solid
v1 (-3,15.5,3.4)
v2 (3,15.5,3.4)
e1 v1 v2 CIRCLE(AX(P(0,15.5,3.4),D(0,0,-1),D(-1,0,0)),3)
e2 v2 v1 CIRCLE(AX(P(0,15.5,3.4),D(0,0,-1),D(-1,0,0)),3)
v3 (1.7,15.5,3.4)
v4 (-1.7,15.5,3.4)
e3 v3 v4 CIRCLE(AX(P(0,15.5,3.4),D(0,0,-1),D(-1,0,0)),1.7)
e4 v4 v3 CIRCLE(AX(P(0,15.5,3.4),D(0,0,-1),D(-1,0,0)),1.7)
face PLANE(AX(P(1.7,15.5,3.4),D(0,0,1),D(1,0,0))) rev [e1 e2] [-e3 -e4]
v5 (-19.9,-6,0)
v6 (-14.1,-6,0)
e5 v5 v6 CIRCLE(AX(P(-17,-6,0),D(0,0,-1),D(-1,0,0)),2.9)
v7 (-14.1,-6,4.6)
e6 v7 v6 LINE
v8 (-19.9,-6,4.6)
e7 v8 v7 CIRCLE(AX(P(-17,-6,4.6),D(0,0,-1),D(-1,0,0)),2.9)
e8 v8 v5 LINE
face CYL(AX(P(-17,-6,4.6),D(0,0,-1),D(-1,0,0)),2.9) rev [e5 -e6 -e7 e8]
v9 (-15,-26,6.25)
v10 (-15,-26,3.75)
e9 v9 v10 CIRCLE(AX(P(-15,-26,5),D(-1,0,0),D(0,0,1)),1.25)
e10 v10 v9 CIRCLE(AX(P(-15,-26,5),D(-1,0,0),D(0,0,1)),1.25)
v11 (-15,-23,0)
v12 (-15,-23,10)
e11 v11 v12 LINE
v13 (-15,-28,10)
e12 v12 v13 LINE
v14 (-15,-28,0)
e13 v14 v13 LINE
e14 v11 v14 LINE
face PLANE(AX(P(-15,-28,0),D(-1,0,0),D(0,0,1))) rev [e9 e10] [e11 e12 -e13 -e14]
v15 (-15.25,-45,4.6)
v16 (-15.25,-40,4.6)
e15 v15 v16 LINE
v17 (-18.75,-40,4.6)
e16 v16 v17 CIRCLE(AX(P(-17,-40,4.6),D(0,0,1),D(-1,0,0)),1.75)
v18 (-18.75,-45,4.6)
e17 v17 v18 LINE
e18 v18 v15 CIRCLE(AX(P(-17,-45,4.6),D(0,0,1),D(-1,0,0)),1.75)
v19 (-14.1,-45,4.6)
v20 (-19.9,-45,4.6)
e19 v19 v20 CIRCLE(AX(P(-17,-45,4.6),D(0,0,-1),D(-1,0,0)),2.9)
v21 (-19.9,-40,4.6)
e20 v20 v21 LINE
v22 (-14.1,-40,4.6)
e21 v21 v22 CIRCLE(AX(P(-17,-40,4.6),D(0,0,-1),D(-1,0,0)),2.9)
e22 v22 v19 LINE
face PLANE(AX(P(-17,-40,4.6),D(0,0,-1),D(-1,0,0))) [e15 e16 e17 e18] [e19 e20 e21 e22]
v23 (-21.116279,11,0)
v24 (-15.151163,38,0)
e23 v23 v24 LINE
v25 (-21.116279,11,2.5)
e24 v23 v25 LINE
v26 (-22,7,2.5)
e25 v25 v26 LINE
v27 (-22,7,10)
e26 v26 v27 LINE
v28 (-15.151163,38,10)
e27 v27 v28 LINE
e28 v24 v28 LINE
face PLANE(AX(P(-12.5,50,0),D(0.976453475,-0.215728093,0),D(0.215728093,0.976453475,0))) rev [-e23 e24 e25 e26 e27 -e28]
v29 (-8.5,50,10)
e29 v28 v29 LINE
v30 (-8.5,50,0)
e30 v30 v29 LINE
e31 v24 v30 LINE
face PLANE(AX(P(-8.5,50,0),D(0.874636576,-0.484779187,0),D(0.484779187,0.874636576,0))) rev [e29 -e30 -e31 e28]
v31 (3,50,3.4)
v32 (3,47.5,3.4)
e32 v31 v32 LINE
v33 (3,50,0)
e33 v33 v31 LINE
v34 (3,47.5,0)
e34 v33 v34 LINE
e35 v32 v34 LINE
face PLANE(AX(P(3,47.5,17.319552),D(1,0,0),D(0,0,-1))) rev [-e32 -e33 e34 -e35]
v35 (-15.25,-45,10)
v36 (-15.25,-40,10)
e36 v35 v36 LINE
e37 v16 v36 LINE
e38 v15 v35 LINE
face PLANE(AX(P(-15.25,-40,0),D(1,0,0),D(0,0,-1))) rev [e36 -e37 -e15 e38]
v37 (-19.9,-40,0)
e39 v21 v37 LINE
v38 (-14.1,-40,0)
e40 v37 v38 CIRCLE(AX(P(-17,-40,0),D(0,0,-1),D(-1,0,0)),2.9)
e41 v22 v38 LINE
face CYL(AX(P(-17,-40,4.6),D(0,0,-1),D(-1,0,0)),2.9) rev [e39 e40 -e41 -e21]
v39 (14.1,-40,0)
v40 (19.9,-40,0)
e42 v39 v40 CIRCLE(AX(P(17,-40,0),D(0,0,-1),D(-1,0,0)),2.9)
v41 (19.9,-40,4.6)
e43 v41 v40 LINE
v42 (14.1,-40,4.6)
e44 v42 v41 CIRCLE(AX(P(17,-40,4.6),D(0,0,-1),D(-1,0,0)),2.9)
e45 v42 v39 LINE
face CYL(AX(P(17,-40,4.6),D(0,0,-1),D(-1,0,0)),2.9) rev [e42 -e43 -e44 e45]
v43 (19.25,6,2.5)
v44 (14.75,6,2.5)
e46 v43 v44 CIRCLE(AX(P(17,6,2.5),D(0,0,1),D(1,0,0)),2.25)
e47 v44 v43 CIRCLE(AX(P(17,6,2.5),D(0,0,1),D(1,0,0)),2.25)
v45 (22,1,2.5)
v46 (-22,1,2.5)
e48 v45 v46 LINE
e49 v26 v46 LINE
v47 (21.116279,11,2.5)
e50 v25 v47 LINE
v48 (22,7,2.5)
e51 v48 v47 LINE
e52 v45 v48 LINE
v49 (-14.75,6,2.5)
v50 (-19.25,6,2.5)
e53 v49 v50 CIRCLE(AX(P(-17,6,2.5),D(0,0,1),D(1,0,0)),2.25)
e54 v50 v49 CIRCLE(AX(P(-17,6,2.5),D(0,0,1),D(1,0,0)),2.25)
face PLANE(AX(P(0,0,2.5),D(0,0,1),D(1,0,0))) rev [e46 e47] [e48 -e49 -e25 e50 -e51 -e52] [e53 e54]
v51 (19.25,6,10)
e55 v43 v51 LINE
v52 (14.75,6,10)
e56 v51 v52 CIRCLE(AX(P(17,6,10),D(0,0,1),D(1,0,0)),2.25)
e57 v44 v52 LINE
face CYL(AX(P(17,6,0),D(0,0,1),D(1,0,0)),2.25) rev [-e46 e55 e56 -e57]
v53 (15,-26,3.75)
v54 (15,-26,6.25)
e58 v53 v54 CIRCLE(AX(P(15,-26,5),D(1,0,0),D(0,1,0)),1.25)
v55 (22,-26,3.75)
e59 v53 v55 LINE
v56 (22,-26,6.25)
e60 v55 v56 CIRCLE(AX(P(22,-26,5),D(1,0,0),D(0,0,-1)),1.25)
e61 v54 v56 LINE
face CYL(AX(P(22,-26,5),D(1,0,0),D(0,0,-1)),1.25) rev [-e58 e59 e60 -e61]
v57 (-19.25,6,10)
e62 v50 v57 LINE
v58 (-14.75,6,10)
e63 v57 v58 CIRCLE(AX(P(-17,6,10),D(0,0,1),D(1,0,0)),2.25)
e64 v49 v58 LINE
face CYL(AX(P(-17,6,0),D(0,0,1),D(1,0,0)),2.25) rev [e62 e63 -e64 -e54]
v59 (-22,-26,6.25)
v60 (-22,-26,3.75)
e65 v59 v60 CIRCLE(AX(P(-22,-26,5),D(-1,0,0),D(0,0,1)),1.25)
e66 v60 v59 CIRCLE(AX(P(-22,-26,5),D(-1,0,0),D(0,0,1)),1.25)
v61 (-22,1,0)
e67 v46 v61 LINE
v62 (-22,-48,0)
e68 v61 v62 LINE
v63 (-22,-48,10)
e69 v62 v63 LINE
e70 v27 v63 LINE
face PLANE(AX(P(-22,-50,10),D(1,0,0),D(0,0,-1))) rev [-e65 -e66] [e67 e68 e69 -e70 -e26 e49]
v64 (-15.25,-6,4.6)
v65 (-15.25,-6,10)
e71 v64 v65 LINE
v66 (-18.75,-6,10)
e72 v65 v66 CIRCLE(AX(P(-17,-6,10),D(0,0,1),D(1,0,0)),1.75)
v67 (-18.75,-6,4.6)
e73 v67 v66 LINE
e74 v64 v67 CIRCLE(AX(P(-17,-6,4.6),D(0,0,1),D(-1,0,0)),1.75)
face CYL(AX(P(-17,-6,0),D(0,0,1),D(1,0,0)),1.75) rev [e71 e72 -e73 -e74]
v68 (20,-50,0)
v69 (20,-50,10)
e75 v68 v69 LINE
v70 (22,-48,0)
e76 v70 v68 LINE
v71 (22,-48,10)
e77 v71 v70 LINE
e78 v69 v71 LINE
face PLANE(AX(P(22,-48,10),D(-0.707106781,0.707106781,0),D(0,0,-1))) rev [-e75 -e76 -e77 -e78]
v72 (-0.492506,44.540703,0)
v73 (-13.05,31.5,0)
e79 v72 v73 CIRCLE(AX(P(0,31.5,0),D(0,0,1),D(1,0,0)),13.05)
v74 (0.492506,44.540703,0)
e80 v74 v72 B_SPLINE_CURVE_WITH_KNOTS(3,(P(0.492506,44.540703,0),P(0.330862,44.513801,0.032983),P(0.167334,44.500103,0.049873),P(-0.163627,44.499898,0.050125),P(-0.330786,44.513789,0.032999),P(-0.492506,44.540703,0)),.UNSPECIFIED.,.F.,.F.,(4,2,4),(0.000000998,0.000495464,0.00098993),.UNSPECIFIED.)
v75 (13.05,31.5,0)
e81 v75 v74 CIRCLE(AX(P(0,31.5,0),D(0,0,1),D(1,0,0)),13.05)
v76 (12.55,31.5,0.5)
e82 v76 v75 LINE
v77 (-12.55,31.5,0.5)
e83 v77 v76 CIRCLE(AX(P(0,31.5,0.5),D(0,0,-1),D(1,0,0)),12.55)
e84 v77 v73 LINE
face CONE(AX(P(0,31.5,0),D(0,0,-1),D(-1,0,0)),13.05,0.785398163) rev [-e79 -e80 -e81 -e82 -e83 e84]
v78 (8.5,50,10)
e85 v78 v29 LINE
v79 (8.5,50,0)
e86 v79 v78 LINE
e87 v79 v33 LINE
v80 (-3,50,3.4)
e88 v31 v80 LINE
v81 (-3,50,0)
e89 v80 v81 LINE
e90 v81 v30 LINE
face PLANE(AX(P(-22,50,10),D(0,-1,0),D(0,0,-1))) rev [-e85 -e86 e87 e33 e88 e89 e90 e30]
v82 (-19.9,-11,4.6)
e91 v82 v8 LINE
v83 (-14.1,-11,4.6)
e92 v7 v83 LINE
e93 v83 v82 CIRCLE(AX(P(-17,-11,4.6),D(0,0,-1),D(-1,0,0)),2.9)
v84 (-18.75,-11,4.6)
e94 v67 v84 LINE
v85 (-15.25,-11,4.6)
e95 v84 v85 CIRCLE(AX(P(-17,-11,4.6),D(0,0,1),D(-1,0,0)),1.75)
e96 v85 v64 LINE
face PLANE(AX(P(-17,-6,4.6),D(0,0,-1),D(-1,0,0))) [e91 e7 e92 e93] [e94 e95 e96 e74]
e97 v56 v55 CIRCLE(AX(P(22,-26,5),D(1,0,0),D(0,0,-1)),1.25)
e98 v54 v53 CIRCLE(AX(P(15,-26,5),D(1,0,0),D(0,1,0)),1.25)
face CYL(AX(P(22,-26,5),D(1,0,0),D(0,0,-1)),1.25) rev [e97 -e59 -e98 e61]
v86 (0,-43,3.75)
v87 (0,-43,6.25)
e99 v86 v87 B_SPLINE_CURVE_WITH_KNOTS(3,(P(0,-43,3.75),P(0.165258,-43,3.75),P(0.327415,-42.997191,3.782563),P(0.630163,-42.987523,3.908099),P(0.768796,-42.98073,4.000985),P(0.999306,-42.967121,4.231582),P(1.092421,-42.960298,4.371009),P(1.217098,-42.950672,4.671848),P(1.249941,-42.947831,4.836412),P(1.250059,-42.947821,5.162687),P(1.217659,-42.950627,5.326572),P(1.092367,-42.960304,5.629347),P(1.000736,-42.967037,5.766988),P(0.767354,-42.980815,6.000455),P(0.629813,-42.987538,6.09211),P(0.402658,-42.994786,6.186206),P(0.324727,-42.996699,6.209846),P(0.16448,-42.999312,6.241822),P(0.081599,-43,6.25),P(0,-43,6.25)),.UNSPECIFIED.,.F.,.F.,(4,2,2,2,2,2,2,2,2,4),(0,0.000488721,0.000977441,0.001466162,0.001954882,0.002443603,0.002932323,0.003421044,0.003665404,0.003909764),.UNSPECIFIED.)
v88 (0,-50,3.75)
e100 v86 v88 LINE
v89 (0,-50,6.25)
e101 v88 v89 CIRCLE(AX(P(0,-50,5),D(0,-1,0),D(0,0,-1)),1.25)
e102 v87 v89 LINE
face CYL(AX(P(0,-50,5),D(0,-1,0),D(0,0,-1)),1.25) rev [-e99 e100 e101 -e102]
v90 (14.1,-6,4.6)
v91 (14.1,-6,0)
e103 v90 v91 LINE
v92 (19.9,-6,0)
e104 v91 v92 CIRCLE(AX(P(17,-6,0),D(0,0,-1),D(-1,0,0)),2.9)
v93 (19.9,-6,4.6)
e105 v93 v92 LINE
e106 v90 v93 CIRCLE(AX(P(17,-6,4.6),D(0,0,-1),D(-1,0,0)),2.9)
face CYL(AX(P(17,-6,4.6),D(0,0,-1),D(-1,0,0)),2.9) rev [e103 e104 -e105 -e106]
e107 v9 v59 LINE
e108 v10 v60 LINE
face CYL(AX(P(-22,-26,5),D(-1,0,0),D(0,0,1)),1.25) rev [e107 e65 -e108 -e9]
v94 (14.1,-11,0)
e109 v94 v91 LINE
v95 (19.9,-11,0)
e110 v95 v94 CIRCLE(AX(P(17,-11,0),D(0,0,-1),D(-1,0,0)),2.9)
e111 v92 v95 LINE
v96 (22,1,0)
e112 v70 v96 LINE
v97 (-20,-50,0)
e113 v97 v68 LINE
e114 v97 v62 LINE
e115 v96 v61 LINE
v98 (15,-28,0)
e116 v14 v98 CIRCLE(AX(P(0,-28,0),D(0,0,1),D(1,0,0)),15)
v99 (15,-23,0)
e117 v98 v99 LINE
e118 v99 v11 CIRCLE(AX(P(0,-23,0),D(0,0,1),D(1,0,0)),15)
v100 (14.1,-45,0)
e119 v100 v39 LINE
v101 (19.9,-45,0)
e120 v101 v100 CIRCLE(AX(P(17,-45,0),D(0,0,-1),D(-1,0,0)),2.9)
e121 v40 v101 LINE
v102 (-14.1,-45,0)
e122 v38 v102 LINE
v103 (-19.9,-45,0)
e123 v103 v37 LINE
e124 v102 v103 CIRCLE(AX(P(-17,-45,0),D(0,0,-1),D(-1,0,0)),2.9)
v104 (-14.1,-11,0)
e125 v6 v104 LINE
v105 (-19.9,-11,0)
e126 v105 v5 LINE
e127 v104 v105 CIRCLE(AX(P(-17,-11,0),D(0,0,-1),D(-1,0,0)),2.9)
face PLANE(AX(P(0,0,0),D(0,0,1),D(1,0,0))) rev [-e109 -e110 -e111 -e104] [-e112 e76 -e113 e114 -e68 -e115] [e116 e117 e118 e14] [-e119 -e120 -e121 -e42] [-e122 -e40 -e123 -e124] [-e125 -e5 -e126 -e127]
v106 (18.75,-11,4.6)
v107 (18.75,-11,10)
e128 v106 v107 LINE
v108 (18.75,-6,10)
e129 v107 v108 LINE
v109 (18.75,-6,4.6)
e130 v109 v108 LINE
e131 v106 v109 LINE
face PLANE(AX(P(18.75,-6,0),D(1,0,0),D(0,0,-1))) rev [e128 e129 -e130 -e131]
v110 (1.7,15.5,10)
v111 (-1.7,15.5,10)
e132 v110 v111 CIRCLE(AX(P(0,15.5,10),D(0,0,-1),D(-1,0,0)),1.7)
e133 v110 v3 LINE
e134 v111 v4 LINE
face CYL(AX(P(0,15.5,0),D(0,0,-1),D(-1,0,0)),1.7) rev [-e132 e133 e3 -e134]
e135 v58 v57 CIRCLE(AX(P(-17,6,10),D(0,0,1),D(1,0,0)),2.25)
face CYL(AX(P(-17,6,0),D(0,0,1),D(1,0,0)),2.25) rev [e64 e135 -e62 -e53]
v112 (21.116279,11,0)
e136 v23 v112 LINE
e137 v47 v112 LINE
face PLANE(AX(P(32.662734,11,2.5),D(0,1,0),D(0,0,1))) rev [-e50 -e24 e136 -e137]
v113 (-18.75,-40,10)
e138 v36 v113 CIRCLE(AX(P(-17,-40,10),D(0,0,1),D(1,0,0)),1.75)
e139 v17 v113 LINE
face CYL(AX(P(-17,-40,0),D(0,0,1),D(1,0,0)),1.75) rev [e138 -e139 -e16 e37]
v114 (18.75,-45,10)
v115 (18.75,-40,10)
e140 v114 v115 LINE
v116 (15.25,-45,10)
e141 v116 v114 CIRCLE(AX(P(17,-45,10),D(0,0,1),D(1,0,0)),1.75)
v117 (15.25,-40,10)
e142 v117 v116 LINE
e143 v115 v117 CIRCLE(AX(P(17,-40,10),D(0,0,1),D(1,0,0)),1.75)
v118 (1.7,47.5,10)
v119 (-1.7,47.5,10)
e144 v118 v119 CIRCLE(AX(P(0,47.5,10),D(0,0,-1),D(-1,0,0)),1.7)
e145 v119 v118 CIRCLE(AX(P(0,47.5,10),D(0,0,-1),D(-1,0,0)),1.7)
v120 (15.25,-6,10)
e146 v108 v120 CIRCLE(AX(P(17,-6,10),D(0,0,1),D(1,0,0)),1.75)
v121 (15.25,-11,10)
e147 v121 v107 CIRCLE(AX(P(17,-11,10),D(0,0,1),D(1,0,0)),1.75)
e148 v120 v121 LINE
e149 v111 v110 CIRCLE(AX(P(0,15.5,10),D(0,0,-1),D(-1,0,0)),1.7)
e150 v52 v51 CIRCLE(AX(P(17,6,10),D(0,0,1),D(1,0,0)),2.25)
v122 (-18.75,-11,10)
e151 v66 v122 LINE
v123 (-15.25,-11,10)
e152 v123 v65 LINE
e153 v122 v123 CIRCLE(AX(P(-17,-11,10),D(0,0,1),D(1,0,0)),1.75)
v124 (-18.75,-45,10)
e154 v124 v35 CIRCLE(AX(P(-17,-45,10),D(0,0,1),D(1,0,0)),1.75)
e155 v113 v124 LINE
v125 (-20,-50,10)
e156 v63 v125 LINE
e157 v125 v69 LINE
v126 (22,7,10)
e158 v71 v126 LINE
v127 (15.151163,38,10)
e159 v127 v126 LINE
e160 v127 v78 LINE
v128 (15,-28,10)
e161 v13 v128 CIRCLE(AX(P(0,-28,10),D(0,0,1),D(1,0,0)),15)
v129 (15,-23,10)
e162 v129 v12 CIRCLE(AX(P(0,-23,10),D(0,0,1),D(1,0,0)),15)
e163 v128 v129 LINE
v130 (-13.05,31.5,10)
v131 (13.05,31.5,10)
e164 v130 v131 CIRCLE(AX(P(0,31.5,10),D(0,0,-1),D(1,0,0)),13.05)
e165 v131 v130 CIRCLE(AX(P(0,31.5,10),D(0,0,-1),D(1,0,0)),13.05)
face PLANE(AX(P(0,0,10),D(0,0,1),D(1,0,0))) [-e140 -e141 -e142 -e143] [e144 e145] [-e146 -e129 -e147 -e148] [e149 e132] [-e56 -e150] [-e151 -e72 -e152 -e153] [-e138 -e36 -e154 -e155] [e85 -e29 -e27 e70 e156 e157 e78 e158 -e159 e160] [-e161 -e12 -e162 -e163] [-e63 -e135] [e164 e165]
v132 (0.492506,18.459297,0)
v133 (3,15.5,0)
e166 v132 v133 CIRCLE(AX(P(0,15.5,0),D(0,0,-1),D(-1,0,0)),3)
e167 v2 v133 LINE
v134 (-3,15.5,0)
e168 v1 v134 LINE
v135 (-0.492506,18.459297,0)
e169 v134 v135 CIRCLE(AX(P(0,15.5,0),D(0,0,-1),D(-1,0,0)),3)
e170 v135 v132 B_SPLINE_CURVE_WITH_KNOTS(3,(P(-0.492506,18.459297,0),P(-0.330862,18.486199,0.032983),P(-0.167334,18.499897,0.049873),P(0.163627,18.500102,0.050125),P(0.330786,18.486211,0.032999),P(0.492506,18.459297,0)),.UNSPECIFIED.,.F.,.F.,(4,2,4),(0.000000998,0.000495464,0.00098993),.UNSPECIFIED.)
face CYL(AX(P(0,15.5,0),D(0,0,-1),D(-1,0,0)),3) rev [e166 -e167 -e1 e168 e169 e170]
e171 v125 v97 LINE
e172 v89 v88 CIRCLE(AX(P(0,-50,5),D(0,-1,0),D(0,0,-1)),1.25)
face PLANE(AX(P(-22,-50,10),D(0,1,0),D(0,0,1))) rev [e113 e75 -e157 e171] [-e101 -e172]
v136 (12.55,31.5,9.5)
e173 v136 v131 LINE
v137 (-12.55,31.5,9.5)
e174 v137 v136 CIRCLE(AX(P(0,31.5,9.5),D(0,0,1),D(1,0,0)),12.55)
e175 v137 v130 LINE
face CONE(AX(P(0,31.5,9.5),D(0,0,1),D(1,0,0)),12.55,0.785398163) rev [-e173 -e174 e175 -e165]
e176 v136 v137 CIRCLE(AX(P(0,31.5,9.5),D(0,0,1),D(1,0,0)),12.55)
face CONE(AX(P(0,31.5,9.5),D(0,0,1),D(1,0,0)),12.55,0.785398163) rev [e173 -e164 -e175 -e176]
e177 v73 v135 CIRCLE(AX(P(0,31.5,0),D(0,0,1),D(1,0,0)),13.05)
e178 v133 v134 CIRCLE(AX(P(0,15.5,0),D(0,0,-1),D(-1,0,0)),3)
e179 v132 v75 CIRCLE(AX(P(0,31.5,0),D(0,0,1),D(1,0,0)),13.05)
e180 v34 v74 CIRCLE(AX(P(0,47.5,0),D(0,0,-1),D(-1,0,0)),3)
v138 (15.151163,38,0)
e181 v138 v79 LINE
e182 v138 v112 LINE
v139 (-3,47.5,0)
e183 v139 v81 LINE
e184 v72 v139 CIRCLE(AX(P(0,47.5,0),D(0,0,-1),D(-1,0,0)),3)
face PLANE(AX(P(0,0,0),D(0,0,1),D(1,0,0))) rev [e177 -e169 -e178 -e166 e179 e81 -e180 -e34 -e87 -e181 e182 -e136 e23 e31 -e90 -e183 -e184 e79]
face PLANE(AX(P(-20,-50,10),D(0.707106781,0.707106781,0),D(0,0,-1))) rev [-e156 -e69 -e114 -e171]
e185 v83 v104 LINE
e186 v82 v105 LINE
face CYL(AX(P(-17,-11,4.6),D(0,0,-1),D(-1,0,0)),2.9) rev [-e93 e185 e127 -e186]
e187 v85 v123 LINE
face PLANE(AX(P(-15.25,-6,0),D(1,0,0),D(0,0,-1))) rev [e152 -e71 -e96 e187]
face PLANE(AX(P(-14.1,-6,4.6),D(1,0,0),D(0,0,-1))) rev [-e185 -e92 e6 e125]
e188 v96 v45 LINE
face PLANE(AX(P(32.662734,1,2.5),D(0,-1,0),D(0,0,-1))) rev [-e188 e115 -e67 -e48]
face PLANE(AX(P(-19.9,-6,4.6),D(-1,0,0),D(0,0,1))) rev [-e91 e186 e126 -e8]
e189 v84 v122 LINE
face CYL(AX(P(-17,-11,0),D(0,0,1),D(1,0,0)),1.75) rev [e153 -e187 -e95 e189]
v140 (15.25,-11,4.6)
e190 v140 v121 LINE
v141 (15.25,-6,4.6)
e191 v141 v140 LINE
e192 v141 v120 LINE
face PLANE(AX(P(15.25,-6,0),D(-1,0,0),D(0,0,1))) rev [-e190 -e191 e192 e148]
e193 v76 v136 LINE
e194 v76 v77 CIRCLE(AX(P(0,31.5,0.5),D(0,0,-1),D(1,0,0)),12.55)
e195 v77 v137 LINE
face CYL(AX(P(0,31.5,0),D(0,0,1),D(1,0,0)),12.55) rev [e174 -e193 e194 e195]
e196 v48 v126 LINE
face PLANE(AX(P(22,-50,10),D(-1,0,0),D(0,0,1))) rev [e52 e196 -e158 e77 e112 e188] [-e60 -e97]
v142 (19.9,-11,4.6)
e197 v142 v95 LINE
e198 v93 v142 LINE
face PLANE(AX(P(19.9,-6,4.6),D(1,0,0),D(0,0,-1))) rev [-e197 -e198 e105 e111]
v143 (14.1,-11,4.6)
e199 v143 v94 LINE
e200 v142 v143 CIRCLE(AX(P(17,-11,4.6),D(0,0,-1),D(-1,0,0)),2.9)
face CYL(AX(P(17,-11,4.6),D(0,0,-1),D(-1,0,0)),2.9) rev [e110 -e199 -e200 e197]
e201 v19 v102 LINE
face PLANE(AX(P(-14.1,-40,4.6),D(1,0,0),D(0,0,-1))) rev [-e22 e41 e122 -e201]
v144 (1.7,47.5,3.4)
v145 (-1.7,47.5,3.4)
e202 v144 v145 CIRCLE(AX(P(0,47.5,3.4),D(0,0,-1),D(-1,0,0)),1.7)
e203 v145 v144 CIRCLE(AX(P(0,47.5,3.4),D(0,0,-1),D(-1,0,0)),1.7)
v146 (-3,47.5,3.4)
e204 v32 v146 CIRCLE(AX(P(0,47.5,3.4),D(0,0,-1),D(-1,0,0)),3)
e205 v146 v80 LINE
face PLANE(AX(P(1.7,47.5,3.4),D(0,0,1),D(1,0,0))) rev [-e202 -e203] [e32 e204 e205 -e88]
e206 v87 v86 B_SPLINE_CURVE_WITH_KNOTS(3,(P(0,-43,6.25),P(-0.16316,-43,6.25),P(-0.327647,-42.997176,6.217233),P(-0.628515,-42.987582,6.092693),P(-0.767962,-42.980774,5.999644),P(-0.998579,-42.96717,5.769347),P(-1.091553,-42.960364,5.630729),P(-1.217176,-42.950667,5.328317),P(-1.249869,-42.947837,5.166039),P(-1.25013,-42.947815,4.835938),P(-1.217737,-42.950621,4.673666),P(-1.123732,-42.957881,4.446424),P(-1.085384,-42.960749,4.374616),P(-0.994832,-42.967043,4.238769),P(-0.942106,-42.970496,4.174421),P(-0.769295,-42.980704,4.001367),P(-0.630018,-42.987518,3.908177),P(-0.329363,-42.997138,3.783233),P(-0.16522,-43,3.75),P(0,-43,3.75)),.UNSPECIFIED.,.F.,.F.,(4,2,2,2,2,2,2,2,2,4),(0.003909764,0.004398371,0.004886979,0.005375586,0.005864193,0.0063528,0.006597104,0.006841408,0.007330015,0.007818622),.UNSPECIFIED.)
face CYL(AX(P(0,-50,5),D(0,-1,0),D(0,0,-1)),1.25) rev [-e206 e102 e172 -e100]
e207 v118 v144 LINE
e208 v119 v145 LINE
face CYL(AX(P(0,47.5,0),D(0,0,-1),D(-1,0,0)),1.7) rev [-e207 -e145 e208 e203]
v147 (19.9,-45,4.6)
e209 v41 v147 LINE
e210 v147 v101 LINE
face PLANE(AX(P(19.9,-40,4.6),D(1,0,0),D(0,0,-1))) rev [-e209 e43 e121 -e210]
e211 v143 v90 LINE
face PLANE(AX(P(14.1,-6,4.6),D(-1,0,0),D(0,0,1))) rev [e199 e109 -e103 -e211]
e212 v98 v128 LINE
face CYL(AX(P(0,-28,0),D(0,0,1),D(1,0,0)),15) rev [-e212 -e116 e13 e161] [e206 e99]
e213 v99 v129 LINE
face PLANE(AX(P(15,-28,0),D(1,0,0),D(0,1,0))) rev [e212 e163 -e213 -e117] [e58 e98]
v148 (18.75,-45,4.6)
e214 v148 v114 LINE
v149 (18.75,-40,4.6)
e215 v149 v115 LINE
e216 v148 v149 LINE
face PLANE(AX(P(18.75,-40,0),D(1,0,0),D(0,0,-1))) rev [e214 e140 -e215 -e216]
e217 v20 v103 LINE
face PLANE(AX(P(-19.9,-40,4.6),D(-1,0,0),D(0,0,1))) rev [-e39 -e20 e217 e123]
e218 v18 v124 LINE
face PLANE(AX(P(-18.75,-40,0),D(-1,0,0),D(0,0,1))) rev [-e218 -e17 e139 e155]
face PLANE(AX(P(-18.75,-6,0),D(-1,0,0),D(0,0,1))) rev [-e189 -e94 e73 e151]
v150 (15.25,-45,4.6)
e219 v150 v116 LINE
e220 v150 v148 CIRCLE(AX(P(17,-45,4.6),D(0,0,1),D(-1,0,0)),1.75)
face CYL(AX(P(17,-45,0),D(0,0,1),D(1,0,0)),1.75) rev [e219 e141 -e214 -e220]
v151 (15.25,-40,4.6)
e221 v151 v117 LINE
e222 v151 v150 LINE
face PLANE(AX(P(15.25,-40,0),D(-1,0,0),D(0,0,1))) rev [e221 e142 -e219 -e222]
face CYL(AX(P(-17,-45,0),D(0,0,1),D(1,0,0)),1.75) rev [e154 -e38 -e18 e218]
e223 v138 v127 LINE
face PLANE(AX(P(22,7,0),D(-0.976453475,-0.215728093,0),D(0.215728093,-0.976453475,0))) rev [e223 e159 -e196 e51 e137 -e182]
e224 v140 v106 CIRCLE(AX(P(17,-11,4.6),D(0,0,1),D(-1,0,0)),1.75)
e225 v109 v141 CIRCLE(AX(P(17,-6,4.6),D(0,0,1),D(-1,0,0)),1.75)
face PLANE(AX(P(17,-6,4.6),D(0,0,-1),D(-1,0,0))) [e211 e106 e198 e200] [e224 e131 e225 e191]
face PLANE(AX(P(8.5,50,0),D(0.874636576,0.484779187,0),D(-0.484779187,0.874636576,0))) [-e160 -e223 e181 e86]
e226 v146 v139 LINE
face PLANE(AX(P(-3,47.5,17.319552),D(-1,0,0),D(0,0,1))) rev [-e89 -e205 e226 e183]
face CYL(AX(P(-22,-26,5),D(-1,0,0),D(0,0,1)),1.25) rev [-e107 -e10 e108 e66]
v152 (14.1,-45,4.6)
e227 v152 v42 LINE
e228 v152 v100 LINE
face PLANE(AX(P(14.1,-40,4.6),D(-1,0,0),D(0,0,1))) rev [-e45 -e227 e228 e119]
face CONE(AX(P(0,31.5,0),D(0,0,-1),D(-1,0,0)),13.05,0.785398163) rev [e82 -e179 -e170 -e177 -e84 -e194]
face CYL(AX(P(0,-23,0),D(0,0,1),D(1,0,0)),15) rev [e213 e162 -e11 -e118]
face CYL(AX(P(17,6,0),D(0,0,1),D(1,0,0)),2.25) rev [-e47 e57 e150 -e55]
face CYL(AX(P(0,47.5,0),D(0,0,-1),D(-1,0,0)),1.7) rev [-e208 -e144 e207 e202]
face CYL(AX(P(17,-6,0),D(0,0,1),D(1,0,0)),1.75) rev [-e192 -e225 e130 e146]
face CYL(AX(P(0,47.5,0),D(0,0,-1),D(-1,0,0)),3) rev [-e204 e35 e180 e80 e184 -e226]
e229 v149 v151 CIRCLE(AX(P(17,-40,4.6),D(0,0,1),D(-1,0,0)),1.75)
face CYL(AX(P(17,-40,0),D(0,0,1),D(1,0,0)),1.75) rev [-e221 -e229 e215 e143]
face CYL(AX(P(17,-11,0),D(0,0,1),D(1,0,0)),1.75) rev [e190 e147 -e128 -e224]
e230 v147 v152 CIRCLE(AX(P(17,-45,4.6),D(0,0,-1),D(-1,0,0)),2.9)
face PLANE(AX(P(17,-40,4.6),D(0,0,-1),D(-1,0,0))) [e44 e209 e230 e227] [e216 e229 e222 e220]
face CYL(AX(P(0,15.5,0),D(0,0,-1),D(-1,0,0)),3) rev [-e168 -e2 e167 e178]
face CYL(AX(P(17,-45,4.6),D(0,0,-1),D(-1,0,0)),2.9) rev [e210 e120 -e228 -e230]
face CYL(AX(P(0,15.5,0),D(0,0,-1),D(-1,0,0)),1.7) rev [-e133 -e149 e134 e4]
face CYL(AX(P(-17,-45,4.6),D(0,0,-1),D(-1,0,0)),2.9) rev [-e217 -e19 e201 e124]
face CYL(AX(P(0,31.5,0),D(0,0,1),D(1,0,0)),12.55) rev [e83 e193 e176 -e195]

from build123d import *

# Parameters (mm, degrees)
SKETCH1_W                                            = 44
SKETCH1_H                                            = 100
BOSS_EXTRUDE1_DEPTH                                  = 10
SKETCH2_R                                            = 12.55
CUT_EXTRUDE1_DEPTH                                   = 56.533773508
CUT_EXTRUDE3_DEPTH                                   = 56.533773508
CUT_EXTRUDE12_DEPTH                                  = 4.6
LPATTERN1_COUNT                                      = 2
LPATTERN1_PITCH                                      = 34
LPATTERN1_COUNT_DIR2                                 = 2
LPATTERN1_PITCH_DIR2                                 = 34
CHAMFER1_SIZE                                        = 2
CUT_EXTRUDE10_DEPTH                                  = 56.533773508
CUT_EXTRUDE11_DEPTH                                  = 10
M3_TAPPED_HOLE3_D                                    = 2.5
SKETCH27_W                                           = 62.376043996
SKETCH27_H                                           = 10
CUT_EXTRUDE13_DEPTH                                  = 2.5
SKETCH6_R                                            = 2.25
CUT_EXTRUDE5_DEPTH                                   = 10
CHAMFER2_SIZE                                        = 0.5
HOLE_SIZE_PER_SOCKET_HEAD_CAP_SCREW_TYPE_D           = 3.4
HOLE_SIZE_PER_SOCKET_HEAD_CAP_SCREW_TYPE_CBORE_D     = 6
HOLE_SIZE_PER_SOCKET_HEAD_CAP_SCREW_TYPE_CBORE_DEPTH = 3.4
CUT_EXTRUDE14_DEPTH                                  = 3.4
M3_TAPPED_HOLE5_D                                    = 2.5
M3_TAPPED_HOLE5_DEPTH                                = 7.5
M3_TAPPED_HOLE5_TIP                                  = 0.751075774


with BuildPart() as part:
    # Sketch1 → Boss-Extrude1 (new body)
    with BuildSketch(Plane.XY):
        Rectangle(SKETCH1_W, SKETCH1_H)
    extrude(amount=BOSS_EXTRUDE1_DEPTH)

    # Sketch2 → Cut-Extrude1 (cut, through all)
    with BuildSketch(Plane.XY.offset(10)):
        with Locations((0, 31.5)):
            Circle(SKETCH2_R)
        with BuildLine():
            Line((-15, -28), (-15, -23))
            ThreePointArc((-15, -23), (0, -8), (15, -23))
            Line((15, -23), (15, -28))
            ThreePointArc((15, -28), (0, -43), (-15, -28))
        make_face()
    extrude(amount=-CUT_EXTRUDE1_DEPTH, mode=Mode.SUBTRACT)

    # Sketch4 → Cut-Extrude3 (cut, through all)
    with BuildSketch(Plane.XY.offset(10)):
        with BuildLine():
            Line((-15.25, -6), (-15.25, -11))
            ThreePointArc((-15.25, -11), (-17, -12.75), (-18.75, -11))
            Line((-18.75, -11), (-18.75, -6))
            ThreePointArc((-18.75, -6), (-17, -4.25), (-15.25, -6))
        make_face()
        with BuildLine():
            Line((18.75, -6), (18.75, -11))
            ThreePointArc((18.75, -11), (17, -12.75), (15.25, -11))
            Line((15.25, -11), (15.25, -6))
            ThreePointArc((15.25, -6), (17, -4.25), (18.75, -6))
        make_face()
        with BuildLine():
            Line((18.75, -40), (18.75, -45))
            ThreePointArc((18.75, -45), (17, -46.75), (15.25, -45))
            Line((15.25, -45), (15.25, -40))
            ThreePointArc((15.25, -40), (17, -38.25), (18.75, -40))
        make_face()
        with BuildLine():
            Line((-15.25, -40), (-15.25, -45))
            ThreePointArc((-15.25, -45), (-17, -46.75), (-18.75, -45))
            Line((-18.75, -45), (-18.75, -40))
            ThreePointArc((-18.75, -40), (-17, -38.25), (-15.25, -40))
        make_face()
    extrude(amount=-CUT_EXTRUDE3_DEPTH, mode=Mode.SUBTRACT)

    # Sketch20 → Cut-Extrude12 (cut)
    with BuildSketch(Plane(origin=(0, 0, 0), x_dir=(-1, 0, 0), z_dir=(0, 0, -1))):
        with BuildLine():
            Line((19.9, -6), (19.9, -11))
            ThreePointArc((19.9, -11), (17, -13.9), (14.1, -11))
            Line((14.1, -11), (14.1, -6))
            ThreePointArc((14.1, -6), (17, -3.1), (19.9, -6))
        make_face()
    cut_extrude12 = extrude(amount=-CUT_EXTRUDE12_DEPTH, mode=Mode.SUBTRACT)

    # LPattern1: Cut-Extrude12 2 × 2
    with Locations(*[(j * LPATTERN1_PITCH_DIR2, -i * LPATTERN1_PITCH, 0) for i in range(LPATTERN1_COUNT) for j in range(LPATTERN1_COUNT_DIR2) if (i, j) != (0, 0)]):
        add(cut_extrude12, mode=Mode.SUBTRACT)

    # Chamfer1
    chamfer1_edges = [part.edges().sort_by_distance(p)[0] for p in [
        (22, -50, 5),
        (-22, -50, 5),
    ]]
    chamfer(chamfer1_edges, length=CHAMFER1_SIZE)

    # Sketch15 → Cut-Extrude10 (cut, through all)
    with BuildSketch(Plane.XY.offset(10)):
        Polygon((22, 7), (12.5, 50), (22, 50), align=None)
        Polygon((-12.5, 50), (-22, 7), (-22, 50), align=None)
    extrude(amount=-CUT_EXTRUDE10_DEPTH, mode=Mode.SUBTRACT)

    # Sketch16 → Cut-Extrude11 (cut)
    with BuildSketch(Plane.XY.offset(10)):
        Polygon((-12.5, 50), (-8.5, 50), (-15.151162791, 38), align=None)
    cut_extrude11 = extrude(amount=-CUT_EXTRUDE11_DEPTH, mode=Mode.SUBTRACT)

    # Mirror2: Cut-Extrude11 across plane
    add(cut_extrude11.mirror(Plane(origin=(0, 0, 0), x_dir=(0, 0, 1), z_dir=(1, 0, 0))), mode=Mode.SUBTRACT)

    # M3 Tapped Hole3 (through all)
    with Locations(Plane.XY.offset(10)):
        with Locations((0, 47.5), (0, 15.5)):
            Hole(M3_TAPPED_HOLE3_D / 2)

    # Sketch27 → Cut-Extrude13 (cut)
    with BuildSketch(Plane(origin=(0, 0, 0), x_dir=(-1, 0, 0), z_dir=(0, 0, -1))):
        with Locations((-1.474712029, 6)):
            Rectangle(SKETCH27_W, SKETCH27_H)
    extrude(amount=-CUT_EXTRUDE13_DEPTH, mode=Mode.SUBTRACT)

    # Sketch6 → Cut-Extrude5 (cut)
    with BuildSketch(Plane.XY.offset(10)):
        with Locations((-17, 6)):
            Circle(SKETCH6_R)
        with Locations((17, 6)):
            Circle(SKETCH6_R)
    extrude(amount=-CUT_EXTRUDE5_DEPTH, mode=Mode.SUBTRACT)

    # Chamfer2
    chamfer2_edges = [part.edges().sort_by_distance(p)[0] for p in [
        (-12.55, 31.5, 0),
        (-12.55, 31.5, 10),
    ]]
    chamfer(chamfer2_edges, length=CHAMFER2_SIZE)

    # Hole size per socket head cap screw type 1 (through all)
    with Locations(Plane(origin=(0, 0, 0), x_dir=(-1, 0, 0), z_dir=(0, 0, -1))):
        with Locations((0, 47.5), (0, 15.5)):
            CounterBoreHole(HOLE_SIZE_PER_SOCKET_HEAD_CAP_SCREW_TYPE_D / 2, HOLE_SIZE_PER_SOCKET_HEAD_CAP_SCREW_TYPE_CBORE_D / 2, HOLE_SIZE_PER_SOCKET_HEAD_CAP_SCREW_TYPE_CBORE_DEPTH)

    # Sketch30 → Cut-Extrude14 (cut)
    with BuildSketch(Plane(origin=(0, 0, 0), x_dir=(-1, 0, 0), z_dir=(0, 0, -1))):
        with BuildLine():
            Line((-3, 47.5), (-3, 54.060013121))
            ThreePointArc((-3, 54.060013121), (0, 57.060013121), (3, 54.060013121))
            Line((3, 54.060013121), (3, 47.5))
            ThreePointArc((3, 47.5), (0, 44.5), (-3, 47.5))
        make_face()
    extrude(amount=-CUT_EXTRUDE14_DEPTH, mode=Mode.SUBTRACT)

    # Sketch31 → M3 Tapped Hole4 (revolve, cut)
    with BuildSketch(Plane(origin=(22, -26, 5), x_dir=(0, 0, -1), z_dir=(0, 1, 0))):
        Polygon((0, 0), (0, 8.251075774), (1.25, 7.5), (1.25, 0), align=None)
    m3_tapped_hole4 = revolve(axis=Axis((28.35, -26, 5), (-1, 0, 0)), mode=Mode.SUBTRACT)

    # Mirror3: M3 Tapped Hole4 across plane
    add(m3_tapped_hole4.mirror(Plane(origin=(0, 0, 0), x_dir=(0, 0, 1), z_dir=(1, 0, 0))), mode=Mode.SUBTRACT)

    # M3 Tapped Hole5
    with Locations(Plane(origin=(0, -50, 0), x_dir=(-1, 0, 0), z_dir=(0, -1, 0))):
        with Locations((0, -5)):
            Hole(M3_TAPPED_HOLE5_D / 2, depth=M3_TAPPED_HOLE5_DEPTH)
            with Locations((0, 0, -(M3_TAPPED_HOLE5_DEPTH + M3_TAPPED_HOLE5_TIP / 2))):  # 118° drill point
                Cone(0, M3_TAPPED_HOLE5_D / 2, M3_TAPPED_HOLE5_TIP, mode=Mode.SUBTRACT)


solid = part.part
